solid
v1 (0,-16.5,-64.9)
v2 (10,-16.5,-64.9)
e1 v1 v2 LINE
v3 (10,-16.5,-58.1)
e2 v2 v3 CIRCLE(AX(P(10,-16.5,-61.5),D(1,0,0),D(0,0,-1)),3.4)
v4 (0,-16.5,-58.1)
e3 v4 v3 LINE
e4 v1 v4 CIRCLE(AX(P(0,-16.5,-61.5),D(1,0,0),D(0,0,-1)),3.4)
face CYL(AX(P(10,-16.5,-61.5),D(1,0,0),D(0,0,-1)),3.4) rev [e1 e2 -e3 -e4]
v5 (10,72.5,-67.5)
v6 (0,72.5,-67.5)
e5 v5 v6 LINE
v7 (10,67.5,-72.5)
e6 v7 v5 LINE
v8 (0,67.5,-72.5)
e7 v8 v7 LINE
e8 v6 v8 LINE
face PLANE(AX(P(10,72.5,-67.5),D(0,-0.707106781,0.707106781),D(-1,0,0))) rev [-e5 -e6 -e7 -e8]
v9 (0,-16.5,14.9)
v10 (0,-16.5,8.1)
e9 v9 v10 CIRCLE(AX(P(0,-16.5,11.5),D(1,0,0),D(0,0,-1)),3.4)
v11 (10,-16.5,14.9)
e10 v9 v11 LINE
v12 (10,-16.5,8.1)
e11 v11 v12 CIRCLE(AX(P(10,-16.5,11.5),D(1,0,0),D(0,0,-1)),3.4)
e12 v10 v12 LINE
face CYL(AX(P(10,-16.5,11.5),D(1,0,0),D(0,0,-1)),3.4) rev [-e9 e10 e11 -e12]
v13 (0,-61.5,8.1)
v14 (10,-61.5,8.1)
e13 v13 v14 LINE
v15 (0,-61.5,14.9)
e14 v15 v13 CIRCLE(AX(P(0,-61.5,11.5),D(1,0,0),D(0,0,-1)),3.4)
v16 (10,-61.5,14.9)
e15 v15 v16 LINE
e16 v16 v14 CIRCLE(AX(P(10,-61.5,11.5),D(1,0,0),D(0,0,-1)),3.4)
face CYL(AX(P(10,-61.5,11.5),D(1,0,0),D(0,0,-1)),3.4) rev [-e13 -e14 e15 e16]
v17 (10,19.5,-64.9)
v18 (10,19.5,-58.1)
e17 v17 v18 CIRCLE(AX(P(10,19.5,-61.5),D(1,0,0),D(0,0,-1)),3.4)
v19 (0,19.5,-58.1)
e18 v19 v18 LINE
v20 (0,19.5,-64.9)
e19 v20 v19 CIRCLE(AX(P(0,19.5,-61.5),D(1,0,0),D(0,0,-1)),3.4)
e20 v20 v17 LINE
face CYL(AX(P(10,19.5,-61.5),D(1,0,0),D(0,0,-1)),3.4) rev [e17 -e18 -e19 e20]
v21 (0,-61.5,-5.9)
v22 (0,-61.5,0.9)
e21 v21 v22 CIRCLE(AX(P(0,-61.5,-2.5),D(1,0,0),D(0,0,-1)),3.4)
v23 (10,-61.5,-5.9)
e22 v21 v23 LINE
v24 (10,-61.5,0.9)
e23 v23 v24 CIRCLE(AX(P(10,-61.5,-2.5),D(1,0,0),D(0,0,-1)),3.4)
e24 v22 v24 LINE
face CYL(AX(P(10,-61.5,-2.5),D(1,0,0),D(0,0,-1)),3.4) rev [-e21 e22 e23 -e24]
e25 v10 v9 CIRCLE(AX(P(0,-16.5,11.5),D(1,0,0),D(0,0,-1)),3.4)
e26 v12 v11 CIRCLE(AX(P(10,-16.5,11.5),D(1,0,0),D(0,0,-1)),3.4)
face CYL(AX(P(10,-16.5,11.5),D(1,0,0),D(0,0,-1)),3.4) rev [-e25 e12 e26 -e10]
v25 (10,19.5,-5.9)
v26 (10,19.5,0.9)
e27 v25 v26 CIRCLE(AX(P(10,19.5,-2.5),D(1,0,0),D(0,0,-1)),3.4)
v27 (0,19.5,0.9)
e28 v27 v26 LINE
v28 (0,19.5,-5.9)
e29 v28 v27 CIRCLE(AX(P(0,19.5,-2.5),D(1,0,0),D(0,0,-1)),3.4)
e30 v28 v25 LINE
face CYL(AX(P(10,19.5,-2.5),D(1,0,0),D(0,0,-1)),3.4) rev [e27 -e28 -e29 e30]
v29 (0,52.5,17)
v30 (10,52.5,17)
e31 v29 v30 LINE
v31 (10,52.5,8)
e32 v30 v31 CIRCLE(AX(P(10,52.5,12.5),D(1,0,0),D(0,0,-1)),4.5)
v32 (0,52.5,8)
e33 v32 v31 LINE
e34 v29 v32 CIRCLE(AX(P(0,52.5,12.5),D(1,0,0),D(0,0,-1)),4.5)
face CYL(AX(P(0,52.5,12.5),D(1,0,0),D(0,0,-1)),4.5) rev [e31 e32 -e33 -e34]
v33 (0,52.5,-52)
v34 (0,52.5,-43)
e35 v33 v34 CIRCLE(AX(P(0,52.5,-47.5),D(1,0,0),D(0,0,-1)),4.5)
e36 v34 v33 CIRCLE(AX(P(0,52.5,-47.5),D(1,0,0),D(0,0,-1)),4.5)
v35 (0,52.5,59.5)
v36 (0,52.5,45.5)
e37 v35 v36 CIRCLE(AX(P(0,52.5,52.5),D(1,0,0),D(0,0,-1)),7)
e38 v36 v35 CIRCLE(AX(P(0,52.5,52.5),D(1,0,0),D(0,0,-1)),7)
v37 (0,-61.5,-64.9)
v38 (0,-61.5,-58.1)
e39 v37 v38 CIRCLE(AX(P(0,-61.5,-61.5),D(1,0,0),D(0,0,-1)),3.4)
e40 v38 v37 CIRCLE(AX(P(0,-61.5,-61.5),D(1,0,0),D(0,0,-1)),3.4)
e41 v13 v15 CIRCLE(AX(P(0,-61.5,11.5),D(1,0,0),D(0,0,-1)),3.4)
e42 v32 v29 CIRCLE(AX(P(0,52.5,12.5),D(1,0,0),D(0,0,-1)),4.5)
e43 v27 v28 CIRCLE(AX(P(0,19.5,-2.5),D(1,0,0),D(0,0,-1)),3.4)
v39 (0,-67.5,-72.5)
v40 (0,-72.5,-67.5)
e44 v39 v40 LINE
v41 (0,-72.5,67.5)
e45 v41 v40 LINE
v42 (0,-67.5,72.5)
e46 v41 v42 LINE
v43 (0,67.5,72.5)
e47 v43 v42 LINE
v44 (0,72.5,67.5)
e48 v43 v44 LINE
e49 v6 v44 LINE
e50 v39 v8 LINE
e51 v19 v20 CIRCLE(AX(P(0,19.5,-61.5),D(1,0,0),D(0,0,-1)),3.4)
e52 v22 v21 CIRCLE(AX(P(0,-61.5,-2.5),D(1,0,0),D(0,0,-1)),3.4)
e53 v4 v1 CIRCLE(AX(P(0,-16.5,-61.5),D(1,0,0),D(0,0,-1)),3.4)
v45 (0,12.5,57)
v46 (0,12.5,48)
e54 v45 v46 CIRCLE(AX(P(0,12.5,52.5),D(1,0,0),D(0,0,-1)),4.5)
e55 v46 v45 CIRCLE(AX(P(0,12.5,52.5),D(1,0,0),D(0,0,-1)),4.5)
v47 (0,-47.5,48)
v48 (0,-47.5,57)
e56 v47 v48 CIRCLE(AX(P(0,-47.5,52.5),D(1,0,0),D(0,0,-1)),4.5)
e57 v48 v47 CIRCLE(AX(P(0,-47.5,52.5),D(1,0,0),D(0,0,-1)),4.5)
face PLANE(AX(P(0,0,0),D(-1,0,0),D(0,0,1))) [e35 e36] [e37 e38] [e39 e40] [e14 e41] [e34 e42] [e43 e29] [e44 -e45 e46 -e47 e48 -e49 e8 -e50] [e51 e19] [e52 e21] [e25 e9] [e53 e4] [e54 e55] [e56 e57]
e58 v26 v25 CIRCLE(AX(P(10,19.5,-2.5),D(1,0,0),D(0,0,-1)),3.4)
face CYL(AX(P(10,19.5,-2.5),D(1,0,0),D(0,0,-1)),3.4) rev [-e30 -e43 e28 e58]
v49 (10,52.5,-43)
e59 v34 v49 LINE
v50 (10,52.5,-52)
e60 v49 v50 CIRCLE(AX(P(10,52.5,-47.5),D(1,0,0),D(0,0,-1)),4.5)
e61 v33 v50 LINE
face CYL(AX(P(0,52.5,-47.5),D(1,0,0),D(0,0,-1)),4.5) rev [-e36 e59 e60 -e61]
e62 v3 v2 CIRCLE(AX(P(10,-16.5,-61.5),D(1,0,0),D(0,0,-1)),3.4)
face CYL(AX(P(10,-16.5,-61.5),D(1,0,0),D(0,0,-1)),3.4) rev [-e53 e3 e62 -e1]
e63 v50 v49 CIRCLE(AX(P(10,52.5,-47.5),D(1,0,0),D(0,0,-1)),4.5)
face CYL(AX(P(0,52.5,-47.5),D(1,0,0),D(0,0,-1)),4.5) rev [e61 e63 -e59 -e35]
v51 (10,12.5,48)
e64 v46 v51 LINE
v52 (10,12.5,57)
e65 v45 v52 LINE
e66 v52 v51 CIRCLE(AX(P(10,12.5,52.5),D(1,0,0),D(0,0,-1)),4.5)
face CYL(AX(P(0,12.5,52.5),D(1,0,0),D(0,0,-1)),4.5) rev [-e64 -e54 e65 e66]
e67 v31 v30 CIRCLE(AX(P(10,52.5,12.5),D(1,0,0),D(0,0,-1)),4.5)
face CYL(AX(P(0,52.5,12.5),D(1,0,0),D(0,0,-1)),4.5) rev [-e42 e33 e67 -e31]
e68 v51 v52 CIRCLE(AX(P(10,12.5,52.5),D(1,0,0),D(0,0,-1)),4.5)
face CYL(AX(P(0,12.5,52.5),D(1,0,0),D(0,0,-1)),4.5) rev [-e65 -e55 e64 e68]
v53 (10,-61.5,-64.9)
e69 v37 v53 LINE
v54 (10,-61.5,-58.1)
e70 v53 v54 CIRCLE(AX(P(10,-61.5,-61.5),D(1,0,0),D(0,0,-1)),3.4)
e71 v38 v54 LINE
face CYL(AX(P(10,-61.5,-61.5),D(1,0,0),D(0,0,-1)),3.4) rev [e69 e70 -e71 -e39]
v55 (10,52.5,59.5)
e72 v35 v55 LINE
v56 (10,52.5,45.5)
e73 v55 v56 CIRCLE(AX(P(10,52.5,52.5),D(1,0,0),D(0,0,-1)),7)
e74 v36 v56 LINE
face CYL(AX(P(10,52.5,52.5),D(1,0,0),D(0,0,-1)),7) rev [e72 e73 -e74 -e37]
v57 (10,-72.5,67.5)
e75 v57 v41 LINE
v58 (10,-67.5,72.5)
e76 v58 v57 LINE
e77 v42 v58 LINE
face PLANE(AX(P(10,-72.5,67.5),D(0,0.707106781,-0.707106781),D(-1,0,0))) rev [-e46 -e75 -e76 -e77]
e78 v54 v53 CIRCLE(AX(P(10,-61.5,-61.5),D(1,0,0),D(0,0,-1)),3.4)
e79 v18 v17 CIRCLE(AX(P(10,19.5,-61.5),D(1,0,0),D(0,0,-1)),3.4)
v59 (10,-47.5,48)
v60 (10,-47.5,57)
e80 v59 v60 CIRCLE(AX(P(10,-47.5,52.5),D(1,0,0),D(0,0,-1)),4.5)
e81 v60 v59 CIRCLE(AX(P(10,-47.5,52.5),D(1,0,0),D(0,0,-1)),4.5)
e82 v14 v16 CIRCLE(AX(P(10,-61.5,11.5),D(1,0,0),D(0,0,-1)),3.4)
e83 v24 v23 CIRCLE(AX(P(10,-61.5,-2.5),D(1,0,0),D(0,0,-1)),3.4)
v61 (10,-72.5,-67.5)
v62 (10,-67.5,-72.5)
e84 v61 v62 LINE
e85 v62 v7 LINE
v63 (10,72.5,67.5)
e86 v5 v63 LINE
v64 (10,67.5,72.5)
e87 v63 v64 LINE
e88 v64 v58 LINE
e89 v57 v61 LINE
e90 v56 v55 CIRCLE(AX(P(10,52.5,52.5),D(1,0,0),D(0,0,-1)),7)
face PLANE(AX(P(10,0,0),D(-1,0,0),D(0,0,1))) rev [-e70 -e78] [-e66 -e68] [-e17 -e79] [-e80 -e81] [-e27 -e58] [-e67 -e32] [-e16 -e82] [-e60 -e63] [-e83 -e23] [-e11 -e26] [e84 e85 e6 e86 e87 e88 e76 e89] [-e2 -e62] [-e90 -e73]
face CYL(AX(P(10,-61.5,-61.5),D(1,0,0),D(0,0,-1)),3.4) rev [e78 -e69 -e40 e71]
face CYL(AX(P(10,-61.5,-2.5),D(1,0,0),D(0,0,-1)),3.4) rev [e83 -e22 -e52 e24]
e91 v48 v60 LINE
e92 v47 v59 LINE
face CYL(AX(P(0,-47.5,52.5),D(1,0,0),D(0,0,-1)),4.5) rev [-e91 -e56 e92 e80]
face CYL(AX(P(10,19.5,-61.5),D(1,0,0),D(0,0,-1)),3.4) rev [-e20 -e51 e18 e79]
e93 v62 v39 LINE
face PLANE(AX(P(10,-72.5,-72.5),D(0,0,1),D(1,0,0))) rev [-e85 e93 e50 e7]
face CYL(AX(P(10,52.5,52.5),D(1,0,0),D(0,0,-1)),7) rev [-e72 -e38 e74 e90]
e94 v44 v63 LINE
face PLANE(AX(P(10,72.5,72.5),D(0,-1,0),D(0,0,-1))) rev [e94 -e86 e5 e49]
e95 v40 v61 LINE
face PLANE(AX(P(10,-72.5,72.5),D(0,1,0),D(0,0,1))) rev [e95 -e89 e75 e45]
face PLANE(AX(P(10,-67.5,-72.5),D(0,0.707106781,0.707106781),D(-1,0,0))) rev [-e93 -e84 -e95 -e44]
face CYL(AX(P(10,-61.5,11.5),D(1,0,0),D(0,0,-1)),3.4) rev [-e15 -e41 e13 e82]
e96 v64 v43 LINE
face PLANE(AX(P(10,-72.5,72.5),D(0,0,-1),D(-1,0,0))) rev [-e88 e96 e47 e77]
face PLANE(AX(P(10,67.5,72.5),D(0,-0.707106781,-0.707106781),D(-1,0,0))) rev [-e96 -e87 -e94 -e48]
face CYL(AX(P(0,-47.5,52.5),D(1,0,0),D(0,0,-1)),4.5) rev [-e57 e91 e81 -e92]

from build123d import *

# Parameters (mm, degrees)
SKETCH_1_W          = 145
SKETCH_1_H          = 145
EXTRUDE_1_DEPTH     = 10
CHAMFER_1_SIZE      = 5
HOLE_WIZARD_M8_1_D  = 6.8
HOLE_WIZARD_M16_1_D = 14
SKETCH_8_R          = 4.5
CUT_EXTRUDE_1_DEPTH = 104.01698889


with BuildPart() as part:
    # 草图1 → 凸台-拉伸1 (new body)
    with BuildSketch(Plane(origin=(0, 0, 0), x_dir=(0, 0, -1), z_dir=(1, 0, 0))):
        Rectangle(SKETCH_1_W, SKETCH_1_H)
    extrude(amount=EXTRUDE_1_DEPTH)

    # 倒角1
    chamfer_1_edges = [part.edges().sort_by_distance(p)[0] for p in [
        (5, -72.5, -72.5),
        (5, -72.5, 72.5),
        (5, 72.5, 72.5),
        (5, 72.5, -72.5),
    ]]
    chamfer(chamfer_1_edges, length=CHAMFER_1_SIZE)

    # M8 螺纹孔1 (through all)
    with Locations(Plane(origin=(10, 0, 0), x_dir=(0, 0, -1), z_dir=(1, 0, 0))):
        with Locations((61.5, -61.5), (2.5, 19.5), (61.5, 19.5), (2.5, -61.5), (-11.5, -61.5), (-11.5, -16.5), (61.5, -16.5)):
            Hole(HOLE_WIZARD_M8_1_D / 2)

    # M16 螺纹孔1 (through all)
    with Locations(Plane(origin=(10, 0, 0), x_dir=(0, 0, -1), z_dir=(1, 0, 0))):
        with Locations((-52.5, 52.5)):
            Hole(HOLE_WIZARD_M16_1_D / 2)

    # 草图8 → 切除-拉伸1 (cut, through all)
    with BuildSketch(Plane(origin=(10, 0, 0), x_dir=(0, 0, -1), z_dir=(1, 0, 0))):
        with Locations((-12.5, 52.5)):
            Circle(SKETCH_8_R)
        with Locations((47.5, 52.5)):
            Circle(SKETCH_8_R)
        with Locations((-52.5, 12.5)):
            Circle(SKETCH_8_R)
        with Locations((-52.5, -47.5)):
            Circle(SKETCH_8_R)
    extrude(amount=-CUT_EXTRUDE_1_DEPTH, mode=Mode.SUBTRACT)


solid = part.part
